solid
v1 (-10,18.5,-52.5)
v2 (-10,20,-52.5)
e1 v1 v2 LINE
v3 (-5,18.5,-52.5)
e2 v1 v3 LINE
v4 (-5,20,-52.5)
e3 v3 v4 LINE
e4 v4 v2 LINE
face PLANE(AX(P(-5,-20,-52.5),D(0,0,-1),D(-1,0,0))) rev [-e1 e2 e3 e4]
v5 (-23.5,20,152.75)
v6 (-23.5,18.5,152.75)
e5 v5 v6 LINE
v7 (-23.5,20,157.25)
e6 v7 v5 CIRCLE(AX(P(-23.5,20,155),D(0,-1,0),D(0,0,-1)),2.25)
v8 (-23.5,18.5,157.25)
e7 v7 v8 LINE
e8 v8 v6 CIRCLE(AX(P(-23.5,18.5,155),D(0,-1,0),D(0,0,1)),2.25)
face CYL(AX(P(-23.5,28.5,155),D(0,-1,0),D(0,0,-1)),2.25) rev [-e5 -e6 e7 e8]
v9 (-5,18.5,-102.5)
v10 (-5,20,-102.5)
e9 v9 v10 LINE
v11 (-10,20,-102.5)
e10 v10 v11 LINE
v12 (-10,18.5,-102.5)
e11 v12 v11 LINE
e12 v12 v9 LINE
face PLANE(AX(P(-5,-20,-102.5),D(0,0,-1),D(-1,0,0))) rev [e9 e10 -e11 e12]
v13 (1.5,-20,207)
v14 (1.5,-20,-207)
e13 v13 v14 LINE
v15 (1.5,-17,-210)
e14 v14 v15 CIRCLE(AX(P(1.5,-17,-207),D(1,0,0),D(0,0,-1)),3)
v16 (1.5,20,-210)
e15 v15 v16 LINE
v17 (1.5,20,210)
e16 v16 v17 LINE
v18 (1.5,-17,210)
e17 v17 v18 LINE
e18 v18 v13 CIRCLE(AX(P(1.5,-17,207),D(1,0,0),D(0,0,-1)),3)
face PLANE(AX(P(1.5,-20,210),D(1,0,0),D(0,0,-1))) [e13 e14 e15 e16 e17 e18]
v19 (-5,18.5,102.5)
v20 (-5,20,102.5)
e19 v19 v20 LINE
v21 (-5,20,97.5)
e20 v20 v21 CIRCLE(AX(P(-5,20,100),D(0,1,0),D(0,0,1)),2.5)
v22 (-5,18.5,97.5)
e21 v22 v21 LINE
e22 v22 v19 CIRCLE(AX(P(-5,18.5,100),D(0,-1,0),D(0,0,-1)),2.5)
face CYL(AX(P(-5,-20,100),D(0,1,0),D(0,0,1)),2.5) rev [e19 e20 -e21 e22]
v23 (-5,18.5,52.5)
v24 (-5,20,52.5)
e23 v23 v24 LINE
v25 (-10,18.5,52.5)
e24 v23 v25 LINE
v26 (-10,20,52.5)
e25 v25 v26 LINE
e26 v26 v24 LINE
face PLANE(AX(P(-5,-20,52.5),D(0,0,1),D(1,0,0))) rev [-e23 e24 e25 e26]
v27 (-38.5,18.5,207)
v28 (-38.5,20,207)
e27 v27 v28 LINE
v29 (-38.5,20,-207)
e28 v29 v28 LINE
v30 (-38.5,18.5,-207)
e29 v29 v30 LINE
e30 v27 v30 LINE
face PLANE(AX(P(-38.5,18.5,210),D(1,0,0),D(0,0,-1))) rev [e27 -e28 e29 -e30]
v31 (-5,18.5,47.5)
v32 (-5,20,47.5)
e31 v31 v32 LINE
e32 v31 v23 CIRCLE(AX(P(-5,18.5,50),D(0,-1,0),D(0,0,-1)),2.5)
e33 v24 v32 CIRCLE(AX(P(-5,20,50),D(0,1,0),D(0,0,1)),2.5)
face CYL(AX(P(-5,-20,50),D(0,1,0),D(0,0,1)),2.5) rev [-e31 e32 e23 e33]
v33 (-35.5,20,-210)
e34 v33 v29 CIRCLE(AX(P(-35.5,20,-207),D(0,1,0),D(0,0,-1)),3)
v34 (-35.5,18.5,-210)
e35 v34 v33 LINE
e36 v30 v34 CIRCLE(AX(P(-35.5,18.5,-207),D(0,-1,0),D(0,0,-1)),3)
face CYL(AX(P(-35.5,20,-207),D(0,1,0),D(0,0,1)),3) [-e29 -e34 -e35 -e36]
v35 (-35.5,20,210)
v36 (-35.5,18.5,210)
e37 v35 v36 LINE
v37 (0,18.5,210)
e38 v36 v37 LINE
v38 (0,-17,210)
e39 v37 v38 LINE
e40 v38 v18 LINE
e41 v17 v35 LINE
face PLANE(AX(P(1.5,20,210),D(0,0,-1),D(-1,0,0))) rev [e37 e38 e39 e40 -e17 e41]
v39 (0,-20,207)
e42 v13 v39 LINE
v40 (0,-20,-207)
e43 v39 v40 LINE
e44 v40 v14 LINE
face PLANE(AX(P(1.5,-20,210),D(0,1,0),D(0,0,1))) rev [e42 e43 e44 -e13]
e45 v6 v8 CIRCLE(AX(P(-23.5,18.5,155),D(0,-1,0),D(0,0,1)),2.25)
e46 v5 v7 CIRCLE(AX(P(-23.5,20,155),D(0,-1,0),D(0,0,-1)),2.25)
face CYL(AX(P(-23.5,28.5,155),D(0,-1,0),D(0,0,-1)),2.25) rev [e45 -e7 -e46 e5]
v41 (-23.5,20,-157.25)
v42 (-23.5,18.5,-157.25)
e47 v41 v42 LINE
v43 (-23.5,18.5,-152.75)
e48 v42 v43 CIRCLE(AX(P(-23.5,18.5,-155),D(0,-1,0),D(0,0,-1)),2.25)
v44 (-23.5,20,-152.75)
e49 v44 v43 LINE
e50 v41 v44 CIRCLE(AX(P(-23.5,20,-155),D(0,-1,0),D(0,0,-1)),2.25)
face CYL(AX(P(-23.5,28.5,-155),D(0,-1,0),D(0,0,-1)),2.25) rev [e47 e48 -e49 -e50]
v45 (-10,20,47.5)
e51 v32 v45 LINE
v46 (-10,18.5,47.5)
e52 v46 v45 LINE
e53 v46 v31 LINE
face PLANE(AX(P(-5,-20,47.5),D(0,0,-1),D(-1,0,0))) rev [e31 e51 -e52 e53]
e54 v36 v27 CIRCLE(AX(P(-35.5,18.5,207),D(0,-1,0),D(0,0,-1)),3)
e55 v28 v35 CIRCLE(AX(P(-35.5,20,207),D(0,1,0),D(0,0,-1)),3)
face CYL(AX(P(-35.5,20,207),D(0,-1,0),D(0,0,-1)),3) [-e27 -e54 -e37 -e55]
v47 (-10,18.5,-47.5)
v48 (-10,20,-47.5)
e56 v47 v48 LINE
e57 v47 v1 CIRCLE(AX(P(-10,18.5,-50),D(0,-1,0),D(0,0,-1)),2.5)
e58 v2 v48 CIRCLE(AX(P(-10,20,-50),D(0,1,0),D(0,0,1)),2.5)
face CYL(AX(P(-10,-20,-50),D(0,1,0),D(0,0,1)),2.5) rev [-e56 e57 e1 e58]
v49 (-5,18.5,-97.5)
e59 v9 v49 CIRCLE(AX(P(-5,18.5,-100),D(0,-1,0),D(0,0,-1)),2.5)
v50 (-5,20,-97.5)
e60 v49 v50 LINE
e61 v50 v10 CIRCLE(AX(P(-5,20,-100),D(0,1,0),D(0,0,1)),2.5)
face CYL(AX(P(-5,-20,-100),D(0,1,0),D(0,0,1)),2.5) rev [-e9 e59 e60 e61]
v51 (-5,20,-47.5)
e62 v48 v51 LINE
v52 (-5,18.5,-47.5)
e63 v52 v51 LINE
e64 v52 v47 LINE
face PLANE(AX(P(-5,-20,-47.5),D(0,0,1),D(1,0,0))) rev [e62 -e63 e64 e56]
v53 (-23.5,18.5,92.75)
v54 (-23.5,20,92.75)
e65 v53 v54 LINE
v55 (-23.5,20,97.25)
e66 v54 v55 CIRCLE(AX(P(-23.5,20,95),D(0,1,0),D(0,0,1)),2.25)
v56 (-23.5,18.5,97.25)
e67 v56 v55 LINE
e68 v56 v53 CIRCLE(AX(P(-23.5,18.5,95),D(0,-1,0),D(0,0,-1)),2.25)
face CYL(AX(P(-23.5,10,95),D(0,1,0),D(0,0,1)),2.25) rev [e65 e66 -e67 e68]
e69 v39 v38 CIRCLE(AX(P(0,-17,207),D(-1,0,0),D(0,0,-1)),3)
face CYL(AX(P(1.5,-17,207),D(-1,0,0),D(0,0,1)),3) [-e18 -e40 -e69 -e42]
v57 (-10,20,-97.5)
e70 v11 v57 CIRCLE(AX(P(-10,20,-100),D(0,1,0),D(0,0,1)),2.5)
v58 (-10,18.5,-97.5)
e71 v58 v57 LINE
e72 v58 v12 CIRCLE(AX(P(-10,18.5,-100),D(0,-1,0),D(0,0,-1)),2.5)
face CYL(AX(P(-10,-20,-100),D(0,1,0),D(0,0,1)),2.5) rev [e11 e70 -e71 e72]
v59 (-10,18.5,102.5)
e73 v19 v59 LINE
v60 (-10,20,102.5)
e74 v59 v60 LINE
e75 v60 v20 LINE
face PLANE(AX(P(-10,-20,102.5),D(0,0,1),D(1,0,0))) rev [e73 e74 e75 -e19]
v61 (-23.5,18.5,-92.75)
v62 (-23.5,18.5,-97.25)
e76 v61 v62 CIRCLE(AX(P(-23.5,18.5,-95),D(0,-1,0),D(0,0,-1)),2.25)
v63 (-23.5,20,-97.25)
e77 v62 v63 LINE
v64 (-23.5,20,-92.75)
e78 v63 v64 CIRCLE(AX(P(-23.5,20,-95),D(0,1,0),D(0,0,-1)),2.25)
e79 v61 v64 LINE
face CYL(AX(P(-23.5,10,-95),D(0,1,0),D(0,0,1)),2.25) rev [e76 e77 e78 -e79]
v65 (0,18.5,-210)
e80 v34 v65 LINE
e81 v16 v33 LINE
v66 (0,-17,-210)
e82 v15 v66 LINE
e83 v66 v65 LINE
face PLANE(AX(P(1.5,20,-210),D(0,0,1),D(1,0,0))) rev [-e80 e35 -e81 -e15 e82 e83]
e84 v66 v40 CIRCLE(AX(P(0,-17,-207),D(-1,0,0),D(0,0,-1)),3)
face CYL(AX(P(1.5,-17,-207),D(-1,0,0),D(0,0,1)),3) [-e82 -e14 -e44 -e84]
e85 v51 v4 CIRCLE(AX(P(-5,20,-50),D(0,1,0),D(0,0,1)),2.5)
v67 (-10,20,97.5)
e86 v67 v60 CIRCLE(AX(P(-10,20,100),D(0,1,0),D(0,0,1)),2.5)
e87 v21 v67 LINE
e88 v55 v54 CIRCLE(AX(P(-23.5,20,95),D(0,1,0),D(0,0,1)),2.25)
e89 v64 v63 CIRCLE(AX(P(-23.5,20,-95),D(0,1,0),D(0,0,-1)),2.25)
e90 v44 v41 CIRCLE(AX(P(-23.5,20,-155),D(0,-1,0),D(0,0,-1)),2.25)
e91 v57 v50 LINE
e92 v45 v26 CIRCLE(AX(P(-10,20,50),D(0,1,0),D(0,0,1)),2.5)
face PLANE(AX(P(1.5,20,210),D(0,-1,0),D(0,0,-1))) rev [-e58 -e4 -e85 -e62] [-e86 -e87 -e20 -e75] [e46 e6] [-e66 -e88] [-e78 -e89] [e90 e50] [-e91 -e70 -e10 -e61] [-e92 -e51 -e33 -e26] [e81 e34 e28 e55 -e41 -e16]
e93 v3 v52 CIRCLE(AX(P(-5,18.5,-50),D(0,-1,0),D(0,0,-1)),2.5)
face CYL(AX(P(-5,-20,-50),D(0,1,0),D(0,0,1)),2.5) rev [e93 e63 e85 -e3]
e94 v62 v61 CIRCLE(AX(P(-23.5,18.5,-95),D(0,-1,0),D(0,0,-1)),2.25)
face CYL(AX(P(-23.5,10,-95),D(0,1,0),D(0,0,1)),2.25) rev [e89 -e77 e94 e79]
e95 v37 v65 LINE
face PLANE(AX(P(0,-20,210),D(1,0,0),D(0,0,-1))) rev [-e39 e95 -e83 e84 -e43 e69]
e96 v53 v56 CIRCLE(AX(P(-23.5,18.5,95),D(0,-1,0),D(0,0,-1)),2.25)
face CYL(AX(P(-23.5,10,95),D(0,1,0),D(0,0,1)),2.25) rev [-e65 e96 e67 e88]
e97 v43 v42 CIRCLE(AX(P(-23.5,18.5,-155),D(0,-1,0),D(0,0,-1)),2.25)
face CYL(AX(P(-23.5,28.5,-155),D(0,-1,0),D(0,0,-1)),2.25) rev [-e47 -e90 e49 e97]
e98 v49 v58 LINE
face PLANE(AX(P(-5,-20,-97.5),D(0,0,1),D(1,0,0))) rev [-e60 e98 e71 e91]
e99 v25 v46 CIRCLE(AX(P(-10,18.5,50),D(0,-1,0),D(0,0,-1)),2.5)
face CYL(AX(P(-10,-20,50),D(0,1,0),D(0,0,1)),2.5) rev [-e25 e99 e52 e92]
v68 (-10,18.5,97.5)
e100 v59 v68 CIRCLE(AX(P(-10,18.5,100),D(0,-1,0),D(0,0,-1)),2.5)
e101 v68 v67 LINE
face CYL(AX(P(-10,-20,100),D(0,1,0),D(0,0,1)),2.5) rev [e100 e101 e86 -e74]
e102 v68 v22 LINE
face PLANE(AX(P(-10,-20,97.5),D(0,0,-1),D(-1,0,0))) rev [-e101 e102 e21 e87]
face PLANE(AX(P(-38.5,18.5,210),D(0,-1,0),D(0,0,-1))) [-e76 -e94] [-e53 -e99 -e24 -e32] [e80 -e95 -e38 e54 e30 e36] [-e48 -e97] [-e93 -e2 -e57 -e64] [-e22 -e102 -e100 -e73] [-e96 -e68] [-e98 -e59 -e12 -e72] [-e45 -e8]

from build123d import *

# Parameters (mm, degrees)
SKETCH_1_W          = 420
SKETCH_1_H          = 40
EXTRUDE_1_DEPTH     = 1.5
SKETCH_2_W          = 420
SKETCH_2_H          = 1.5
EXTRUDE_2_DEPTH     = 40
FILLET_1_R          = 3
SKETCH_3_R          = 2.25
CUT_EXTRUDE_1_DEPTH = 10
SKETCH_6_R          = 2.25
CUT_EXTRUDE_2_DEPTH = 10
CUT_EXTRUDE_3_DEPTH = 218.214755484
CUT_EXTRUDE_4_DEPTH = 218.214755484


with BuildPart() as part:
    # 草图1 → 凸台-拉伸1 (new body)
    with BuildSketch(Plane(origin=(0, 0, 0), x_dir=(0, 0, -1), z_dir=(1, 0, 0))):
        Rectangle(SKETCH_1_W, SKETCH_1_H)
    extrude(amount=EXTRUDE_1_DEPTH)

    # 草图2 → 凸台-拉伸2 (add)
    with BuildSketch(Plane(origin=(1.5, 0, 0), x_dir=(0, 0, -1), z_dir=(1, 0, 0))):
        with Locations((0, 19.25)):
            Rectangle(SKETCH_2_W, SKETCH_2_H)
    extrude(amount=-EXTRUDE_2_DEPTH)

    # 圆角1
    fillet_1_edges = [part.edges().sort_by_distance(p)[0] for p in [
        (-38.5, 19.25, 210),
        (-38.5, 19.25, -210),
        (0.75, -20, -210),
        (0.75, -20, 210),
    ]]
    fillet(fillet_1_edges, radius=FILLET_1_R)

    # 草图3 → 切除-拉伸1 (cut)
    with BuildSketch(Plane(origin=(0, 20, 0), x_dir=(1, 0, 0), z_dir=(0, 1, 0))):
        with Locations(Location((-23.5, -95, 0), (0, 0, 270))):
            Circle(SKETCH_3_R)
        with Locations(Location((-23.5, 95, 0), (0, 0, 90))):
            Circle(SKETCH_3_R)
    extrude(amount=-CUT_EXTRUDE_1_DEPTH, mode=Mode.SUBTRACT)

    # 草图6 → 切除-拉伸2 (cut)
    with BuildSketch(Plane.XZ.offset(-18.5)):
        with Locations(Location((-23.5, -155, 0), (0, 0, 270))):
            Circle(SKETCH_6_R)
        with Locations(Location((-23.5, 155, 0), (0, 0, 270))):
            Circle(SKETCH_6_R)
    extrude(amount=-CUT_EXTRUDE_2_DEPTH, mode=Mode.SUBTRACT)

    # 草图7 → 切除-拉伸3 (cut, through all)
    with BuildSketch(Plane(origin=(0, 20, 0), x_dir=(1, 0, 0), z_dir=(0, 1, 0))):
        with BuildLine():
            Line((-10, -97.5), (-5, -97.5))
            ThreePointArc((-5, -97.5), (-2.5, -100), (-5, -102.5))
            Line((-5, -102.5), (-10, -102.5))
            ThreePointArc((-10, -102.5), (-12.5, -100), (-10, -97.5))
        make_face()
        with BuildLine():
            Line((-5, 47.5), (-10, 47.5))
            ThreePointArc((-10, 47.5), (-12.5, 50), (-10, 52.5))
            Line((-10, 52.5), (-5, 52.5))
            ThreePointArc((-5, 52.5), (-2.5, 50), (-5, 47.5))
        make_face()
    extrude(amount=-CUT_EXTRUDE_3_DEPTH, mode=Mode.SUBTRACT)

    # 草图9 → 切除-拉伸4 (cut, through all)
    with BuildSketch(Plane(origin=(0, 20, 0), x_dir=(1, 0, 0), z_dir=(0, 1, 0))):
        with BuildLine():
            Line((-5, -52.5), (-10, -52.5))
            ThreePointArc((-10, -52.5), (-12.5, -50), (-10, -47.5))
            Line((-10, -47.5), (-5, -47.5))
            ThreePointArc((-5, -47.5), (-2.5, -50), (-5, -52.5))
        make_face()
        with BuildLine():
            Line((-5, 97.5), (-10, 97.5))
            ThreePointArc((-10, 97.5), (-12.5, 100), (-10, 102.5))
            Line((-10, 102.5), (-5, 102.5))
            ThreePointArc((-5, 102.5), (-2.5, 100), (-5, 97.5))
        make_face()
    extrude(amount=-CUT_EXTRUDE_4_DEPTH, mode=Mode.SUBTRACT)


solid = part.part
